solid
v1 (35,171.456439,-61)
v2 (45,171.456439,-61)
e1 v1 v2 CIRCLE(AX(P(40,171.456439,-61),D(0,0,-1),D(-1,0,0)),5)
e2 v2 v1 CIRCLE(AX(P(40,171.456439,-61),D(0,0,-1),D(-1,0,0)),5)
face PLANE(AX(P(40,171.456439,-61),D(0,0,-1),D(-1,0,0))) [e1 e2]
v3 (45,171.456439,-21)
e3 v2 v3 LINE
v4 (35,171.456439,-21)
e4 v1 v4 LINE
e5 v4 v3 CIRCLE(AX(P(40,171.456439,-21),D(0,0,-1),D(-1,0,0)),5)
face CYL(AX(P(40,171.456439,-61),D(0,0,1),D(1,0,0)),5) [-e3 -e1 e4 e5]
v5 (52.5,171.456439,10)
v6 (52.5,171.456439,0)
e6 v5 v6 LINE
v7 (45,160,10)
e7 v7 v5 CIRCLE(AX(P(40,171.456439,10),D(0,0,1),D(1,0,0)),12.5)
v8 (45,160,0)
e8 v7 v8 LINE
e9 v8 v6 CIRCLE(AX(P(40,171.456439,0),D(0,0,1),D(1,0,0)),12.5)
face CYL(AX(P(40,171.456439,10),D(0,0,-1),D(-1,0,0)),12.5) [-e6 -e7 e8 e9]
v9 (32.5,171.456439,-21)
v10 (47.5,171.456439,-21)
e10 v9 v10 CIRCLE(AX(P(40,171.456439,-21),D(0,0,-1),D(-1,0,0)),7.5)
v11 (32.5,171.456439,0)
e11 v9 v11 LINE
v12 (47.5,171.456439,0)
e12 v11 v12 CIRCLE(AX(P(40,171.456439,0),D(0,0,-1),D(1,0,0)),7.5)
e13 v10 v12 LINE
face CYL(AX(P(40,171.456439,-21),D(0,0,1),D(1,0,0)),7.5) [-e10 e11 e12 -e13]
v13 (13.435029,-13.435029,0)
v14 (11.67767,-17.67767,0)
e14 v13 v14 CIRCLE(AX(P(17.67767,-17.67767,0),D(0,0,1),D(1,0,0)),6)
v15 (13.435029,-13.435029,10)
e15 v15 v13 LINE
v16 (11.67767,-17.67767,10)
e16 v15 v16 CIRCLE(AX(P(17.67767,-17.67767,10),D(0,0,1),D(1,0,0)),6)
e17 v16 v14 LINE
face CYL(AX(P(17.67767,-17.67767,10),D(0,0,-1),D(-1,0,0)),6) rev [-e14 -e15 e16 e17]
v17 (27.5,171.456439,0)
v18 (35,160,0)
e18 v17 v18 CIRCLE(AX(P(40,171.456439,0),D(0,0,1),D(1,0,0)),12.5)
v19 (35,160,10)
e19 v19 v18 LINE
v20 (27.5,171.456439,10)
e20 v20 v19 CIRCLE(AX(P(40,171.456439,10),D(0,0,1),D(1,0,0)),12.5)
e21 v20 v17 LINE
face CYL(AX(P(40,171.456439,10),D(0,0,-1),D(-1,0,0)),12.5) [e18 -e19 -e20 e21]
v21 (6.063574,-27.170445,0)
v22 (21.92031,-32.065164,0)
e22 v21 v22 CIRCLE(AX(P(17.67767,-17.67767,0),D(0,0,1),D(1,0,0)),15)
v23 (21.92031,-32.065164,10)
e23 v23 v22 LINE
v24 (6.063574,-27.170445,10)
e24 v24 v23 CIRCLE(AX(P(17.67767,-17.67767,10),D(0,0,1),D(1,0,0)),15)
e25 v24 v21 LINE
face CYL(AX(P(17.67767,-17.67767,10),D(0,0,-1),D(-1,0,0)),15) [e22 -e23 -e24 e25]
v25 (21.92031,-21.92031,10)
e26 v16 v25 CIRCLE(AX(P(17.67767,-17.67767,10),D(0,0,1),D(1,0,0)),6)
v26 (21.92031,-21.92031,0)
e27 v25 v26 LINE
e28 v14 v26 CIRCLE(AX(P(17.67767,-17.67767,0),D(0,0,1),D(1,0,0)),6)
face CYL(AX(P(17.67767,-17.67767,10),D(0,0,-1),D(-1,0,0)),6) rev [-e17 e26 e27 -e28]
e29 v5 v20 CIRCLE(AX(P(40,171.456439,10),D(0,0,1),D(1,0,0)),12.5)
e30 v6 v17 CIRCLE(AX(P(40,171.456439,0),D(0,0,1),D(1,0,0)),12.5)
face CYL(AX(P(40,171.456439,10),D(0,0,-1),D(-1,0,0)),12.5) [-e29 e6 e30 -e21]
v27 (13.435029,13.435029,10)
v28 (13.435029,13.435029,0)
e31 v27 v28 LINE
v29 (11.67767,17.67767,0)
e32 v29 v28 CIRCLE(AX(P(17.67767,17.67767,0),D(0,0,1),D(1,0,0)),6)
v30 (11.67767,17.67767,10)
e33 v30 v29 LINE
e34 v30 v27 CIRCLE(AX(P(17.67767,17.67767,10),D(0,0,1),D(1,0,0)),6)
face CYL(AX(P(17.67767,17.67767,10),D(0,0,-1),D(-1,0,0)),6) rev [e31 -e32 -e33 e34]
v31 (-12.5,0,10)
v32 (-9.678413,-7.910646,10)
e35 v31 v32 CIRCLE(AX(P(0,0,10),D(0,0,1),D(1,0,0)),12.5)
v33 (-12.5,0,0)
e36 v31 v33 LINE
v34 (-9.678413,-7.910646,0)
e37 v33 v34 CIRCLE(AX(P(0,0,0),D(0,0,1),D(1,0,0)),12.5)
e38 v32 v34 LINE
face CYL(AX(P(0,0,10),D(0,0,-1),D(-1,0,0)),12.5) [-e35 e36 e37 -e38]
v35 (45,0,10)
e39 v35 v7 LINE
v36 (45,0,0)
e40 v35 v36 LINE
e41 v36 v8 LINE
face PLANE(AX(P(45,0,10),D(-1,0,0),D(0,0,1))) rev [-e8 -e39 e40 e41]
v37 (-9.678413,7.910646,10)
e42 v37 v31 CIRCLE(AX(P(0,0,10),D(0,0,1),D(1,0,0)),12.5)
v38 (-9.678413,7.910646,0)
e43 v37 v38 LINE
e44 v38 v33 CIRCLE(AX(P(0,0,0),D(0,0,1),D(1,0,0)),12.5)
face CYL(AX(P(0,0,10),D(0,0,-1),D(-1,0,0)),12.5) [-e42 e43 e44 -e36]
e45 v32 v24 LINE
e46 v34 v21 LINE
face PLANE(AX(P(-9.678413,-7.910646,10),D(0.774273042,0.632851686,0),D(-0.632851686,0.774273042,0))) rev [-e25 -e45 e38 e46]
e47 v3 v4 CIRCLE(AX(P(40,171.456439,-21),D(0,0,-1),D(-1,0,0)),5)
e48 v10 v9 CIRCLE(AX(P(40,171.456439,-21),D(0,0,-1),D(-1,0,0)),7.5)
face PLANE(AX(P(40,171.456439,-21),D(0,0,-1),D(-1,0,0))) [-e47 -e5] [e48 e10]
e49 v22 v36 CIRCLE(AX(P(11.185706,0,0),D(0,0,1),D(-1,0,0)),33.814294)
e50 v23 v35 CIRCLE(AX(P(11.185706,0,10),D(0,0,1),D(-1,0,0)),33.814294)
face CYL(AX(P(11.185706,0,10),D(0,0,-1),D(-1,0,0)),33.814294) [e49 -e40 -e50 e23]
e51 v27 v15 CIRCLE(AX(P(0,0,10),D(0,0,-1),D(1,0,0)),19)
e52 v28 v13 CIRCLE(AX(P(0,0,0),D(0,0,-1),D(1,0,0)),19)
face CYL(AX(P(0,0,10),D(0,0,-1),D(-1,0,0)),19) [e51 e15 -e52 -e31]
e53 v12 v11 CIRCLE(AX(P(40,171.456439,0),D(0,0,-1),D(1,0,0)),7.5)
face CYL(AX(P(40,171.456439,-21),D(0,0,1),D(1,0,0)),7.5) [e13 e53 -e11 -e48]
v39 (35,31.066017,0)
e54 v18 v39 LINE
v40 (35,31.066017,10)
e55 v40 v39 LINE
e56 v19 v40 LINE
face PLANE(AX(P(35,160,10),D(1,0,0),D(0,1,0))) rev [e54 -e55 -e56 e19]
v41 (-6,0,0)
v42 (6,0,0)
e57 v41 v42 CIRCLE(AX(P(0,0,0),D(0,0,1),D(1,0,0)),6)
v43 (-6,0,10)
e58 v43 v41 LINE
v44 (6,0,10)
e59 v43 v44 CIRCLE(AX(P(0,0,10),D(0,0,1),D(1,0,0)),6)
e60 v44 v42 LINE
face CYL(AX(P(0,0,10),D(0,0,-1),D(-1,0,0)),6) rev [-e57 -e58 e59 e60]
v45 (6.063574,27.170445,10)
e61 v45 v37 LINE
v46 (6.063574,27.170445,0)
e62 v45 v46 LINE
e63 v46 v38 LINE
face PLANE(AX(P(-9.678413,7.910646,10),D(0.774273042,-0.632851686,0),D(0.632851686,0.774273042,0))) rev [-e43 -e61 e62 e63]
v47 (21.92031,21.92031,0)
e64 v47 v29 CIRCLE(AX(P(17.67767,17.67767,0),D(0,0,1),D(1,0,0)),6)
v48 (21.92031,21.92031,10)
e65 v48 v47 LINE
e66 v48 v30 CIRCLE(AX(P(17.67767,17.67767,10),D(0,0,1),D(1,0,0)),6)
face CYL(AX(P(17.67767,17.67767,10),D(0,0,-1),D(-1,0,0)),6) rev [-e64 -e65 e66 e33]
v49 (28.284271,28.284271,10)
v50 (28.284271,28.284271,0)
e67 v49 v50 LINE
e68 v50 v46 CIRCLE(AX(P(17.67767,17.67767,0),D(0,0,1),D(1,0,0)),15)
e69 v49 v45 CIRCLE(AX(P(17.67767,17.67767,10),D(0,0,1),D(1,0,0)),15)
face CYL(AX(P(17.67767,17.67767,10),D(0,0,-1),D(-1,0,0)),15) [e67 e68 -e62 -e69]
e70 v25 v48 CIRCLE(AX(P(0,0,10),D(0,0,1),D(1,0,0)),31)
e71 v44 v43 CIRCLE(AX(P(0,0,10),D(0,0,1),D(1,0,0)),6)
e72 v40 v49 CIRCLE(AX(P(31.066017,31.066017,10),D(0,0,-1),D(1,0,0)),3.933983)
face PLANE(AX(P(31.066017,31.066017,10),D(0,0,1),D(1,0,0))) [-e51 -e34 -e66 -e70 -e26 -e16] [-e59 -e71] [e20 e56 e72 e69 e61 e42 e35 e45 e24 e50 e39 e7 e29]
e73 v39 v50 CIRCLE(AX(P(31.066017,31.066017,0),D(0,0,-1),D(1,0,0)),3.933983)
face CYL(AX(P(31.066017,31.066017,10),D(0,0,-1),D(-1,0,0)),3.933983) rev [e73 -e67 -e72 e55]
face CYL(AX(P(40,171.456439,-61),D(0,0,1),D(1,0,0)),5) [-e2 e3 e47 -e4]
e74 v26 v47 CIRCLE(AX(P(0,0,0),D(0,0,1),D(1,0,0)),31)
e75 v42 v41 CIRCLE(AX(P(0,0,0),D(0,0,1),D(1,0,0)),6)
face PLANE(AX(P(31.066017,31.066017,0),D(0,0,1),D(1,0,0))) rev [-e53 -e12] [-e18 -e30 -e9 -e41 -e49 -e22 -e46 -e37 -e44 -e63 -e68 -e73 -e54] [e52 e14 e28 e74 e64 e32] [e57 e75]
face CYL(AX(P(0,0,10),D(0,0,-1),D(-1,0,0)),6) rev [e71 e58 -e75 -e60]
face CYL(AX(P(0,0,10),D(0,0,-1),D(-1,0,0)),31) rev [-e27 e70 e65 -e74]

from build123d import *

# Parameters (mm, degrees)
SKETCH_1_R      = 6
EXTRUDE_1_DEPTH = 10
SKETCH_3_R      = 7.5
EXTRUDE_2_DEPTH = 21
SKETCH_4_R      = 5
EXTRUDE_3_DEPTH = 40


with BuildPart() as part:
    # 草图1 → 凸台-拉伸1 (new body)
    with BuildSketch(Plane.XY):
        with BuildLine():
            Line((-9.678413026, 7.910646073), (6.063573898, 27.170444817))
            ThreePointArc((6.063573898, 27.170444817), (16.926727904, 32.658860626), (28.284271247, 28.284271247))
            ThreePointArc((28.284271247, 28.284271247), (32.571487227, 27.431490967), (35, 31.066017178))
            Line((35, 31.066017178), (35, 160))
            ThreePointArc((35, 160), (40, 183.956439237), (45, 160))
            Line((45, 160), (45, 0))
            ThreePointArc((45, 0), (38.630100159, -19.753777039), (21.920310217, -32.0651641))
            ThreePointArc((21.920310217, -32.0651641), (13.253400527, -32.010353988), (6.063573898, -27.170444817))
            Line((6.063573898, -27.170444817), (-9.678413026, -7.910646073))
            ThreePointArc((-9.678413026, -7.910646073), (-12.5, 0), (-9.678413026, 7.910646073))
        make_face()
        Circle(SKETCH_1_R, mode=Mode.SUBTRACT)
        with BuildLine():
            ThreePointArc((21.920310217, -21.920310217), (31, 0), (21.920310217, 21.920310217))
            ThreePointArc((21.920310217, 21.920310217), (13.435028843, 21.920310217), (13.435028843, 13.435028843))
            ThreePointArc((13.435028843, 13.435028843), (19, 0), (13.435028843, -13.435028843))
            ThreePointArc((13.435028843, -13.435028843), (13.435028843, -21.920310217), (21.920310217, -21.920310217))
        make_face(mode=Mode.SUBTRACT)
    extrude(amount=EXTRUDE_1_DEPTH)

    # 草图3 → 凸台-拉伸2 (add)
    with BuildSketch(Plane(origin=(0, 0, 0), x_dir=(-1, 0, 0), z_dir=(0, 0, -1))):
        with Locations(Location((-40, 171.456439237, 0), (0, 0, 180))):
            Circle(SKETCH_3_R)
    extrude(amount=EXTRUDE_2_DEPTH)

    # 草图4 → 凸台-拉伸3 (add)
    with BuildSketch(Plane(origin=(0, 0, -21), x_dir=(-1, 0, 0), z_dir=(0, 0, -1))):
        with Locations((-40, 171.456439237)):
            Circle(SKETCH_4_R)
    extrude(amount=EXTRUDE_3_DEPTH)


solid = part.part
